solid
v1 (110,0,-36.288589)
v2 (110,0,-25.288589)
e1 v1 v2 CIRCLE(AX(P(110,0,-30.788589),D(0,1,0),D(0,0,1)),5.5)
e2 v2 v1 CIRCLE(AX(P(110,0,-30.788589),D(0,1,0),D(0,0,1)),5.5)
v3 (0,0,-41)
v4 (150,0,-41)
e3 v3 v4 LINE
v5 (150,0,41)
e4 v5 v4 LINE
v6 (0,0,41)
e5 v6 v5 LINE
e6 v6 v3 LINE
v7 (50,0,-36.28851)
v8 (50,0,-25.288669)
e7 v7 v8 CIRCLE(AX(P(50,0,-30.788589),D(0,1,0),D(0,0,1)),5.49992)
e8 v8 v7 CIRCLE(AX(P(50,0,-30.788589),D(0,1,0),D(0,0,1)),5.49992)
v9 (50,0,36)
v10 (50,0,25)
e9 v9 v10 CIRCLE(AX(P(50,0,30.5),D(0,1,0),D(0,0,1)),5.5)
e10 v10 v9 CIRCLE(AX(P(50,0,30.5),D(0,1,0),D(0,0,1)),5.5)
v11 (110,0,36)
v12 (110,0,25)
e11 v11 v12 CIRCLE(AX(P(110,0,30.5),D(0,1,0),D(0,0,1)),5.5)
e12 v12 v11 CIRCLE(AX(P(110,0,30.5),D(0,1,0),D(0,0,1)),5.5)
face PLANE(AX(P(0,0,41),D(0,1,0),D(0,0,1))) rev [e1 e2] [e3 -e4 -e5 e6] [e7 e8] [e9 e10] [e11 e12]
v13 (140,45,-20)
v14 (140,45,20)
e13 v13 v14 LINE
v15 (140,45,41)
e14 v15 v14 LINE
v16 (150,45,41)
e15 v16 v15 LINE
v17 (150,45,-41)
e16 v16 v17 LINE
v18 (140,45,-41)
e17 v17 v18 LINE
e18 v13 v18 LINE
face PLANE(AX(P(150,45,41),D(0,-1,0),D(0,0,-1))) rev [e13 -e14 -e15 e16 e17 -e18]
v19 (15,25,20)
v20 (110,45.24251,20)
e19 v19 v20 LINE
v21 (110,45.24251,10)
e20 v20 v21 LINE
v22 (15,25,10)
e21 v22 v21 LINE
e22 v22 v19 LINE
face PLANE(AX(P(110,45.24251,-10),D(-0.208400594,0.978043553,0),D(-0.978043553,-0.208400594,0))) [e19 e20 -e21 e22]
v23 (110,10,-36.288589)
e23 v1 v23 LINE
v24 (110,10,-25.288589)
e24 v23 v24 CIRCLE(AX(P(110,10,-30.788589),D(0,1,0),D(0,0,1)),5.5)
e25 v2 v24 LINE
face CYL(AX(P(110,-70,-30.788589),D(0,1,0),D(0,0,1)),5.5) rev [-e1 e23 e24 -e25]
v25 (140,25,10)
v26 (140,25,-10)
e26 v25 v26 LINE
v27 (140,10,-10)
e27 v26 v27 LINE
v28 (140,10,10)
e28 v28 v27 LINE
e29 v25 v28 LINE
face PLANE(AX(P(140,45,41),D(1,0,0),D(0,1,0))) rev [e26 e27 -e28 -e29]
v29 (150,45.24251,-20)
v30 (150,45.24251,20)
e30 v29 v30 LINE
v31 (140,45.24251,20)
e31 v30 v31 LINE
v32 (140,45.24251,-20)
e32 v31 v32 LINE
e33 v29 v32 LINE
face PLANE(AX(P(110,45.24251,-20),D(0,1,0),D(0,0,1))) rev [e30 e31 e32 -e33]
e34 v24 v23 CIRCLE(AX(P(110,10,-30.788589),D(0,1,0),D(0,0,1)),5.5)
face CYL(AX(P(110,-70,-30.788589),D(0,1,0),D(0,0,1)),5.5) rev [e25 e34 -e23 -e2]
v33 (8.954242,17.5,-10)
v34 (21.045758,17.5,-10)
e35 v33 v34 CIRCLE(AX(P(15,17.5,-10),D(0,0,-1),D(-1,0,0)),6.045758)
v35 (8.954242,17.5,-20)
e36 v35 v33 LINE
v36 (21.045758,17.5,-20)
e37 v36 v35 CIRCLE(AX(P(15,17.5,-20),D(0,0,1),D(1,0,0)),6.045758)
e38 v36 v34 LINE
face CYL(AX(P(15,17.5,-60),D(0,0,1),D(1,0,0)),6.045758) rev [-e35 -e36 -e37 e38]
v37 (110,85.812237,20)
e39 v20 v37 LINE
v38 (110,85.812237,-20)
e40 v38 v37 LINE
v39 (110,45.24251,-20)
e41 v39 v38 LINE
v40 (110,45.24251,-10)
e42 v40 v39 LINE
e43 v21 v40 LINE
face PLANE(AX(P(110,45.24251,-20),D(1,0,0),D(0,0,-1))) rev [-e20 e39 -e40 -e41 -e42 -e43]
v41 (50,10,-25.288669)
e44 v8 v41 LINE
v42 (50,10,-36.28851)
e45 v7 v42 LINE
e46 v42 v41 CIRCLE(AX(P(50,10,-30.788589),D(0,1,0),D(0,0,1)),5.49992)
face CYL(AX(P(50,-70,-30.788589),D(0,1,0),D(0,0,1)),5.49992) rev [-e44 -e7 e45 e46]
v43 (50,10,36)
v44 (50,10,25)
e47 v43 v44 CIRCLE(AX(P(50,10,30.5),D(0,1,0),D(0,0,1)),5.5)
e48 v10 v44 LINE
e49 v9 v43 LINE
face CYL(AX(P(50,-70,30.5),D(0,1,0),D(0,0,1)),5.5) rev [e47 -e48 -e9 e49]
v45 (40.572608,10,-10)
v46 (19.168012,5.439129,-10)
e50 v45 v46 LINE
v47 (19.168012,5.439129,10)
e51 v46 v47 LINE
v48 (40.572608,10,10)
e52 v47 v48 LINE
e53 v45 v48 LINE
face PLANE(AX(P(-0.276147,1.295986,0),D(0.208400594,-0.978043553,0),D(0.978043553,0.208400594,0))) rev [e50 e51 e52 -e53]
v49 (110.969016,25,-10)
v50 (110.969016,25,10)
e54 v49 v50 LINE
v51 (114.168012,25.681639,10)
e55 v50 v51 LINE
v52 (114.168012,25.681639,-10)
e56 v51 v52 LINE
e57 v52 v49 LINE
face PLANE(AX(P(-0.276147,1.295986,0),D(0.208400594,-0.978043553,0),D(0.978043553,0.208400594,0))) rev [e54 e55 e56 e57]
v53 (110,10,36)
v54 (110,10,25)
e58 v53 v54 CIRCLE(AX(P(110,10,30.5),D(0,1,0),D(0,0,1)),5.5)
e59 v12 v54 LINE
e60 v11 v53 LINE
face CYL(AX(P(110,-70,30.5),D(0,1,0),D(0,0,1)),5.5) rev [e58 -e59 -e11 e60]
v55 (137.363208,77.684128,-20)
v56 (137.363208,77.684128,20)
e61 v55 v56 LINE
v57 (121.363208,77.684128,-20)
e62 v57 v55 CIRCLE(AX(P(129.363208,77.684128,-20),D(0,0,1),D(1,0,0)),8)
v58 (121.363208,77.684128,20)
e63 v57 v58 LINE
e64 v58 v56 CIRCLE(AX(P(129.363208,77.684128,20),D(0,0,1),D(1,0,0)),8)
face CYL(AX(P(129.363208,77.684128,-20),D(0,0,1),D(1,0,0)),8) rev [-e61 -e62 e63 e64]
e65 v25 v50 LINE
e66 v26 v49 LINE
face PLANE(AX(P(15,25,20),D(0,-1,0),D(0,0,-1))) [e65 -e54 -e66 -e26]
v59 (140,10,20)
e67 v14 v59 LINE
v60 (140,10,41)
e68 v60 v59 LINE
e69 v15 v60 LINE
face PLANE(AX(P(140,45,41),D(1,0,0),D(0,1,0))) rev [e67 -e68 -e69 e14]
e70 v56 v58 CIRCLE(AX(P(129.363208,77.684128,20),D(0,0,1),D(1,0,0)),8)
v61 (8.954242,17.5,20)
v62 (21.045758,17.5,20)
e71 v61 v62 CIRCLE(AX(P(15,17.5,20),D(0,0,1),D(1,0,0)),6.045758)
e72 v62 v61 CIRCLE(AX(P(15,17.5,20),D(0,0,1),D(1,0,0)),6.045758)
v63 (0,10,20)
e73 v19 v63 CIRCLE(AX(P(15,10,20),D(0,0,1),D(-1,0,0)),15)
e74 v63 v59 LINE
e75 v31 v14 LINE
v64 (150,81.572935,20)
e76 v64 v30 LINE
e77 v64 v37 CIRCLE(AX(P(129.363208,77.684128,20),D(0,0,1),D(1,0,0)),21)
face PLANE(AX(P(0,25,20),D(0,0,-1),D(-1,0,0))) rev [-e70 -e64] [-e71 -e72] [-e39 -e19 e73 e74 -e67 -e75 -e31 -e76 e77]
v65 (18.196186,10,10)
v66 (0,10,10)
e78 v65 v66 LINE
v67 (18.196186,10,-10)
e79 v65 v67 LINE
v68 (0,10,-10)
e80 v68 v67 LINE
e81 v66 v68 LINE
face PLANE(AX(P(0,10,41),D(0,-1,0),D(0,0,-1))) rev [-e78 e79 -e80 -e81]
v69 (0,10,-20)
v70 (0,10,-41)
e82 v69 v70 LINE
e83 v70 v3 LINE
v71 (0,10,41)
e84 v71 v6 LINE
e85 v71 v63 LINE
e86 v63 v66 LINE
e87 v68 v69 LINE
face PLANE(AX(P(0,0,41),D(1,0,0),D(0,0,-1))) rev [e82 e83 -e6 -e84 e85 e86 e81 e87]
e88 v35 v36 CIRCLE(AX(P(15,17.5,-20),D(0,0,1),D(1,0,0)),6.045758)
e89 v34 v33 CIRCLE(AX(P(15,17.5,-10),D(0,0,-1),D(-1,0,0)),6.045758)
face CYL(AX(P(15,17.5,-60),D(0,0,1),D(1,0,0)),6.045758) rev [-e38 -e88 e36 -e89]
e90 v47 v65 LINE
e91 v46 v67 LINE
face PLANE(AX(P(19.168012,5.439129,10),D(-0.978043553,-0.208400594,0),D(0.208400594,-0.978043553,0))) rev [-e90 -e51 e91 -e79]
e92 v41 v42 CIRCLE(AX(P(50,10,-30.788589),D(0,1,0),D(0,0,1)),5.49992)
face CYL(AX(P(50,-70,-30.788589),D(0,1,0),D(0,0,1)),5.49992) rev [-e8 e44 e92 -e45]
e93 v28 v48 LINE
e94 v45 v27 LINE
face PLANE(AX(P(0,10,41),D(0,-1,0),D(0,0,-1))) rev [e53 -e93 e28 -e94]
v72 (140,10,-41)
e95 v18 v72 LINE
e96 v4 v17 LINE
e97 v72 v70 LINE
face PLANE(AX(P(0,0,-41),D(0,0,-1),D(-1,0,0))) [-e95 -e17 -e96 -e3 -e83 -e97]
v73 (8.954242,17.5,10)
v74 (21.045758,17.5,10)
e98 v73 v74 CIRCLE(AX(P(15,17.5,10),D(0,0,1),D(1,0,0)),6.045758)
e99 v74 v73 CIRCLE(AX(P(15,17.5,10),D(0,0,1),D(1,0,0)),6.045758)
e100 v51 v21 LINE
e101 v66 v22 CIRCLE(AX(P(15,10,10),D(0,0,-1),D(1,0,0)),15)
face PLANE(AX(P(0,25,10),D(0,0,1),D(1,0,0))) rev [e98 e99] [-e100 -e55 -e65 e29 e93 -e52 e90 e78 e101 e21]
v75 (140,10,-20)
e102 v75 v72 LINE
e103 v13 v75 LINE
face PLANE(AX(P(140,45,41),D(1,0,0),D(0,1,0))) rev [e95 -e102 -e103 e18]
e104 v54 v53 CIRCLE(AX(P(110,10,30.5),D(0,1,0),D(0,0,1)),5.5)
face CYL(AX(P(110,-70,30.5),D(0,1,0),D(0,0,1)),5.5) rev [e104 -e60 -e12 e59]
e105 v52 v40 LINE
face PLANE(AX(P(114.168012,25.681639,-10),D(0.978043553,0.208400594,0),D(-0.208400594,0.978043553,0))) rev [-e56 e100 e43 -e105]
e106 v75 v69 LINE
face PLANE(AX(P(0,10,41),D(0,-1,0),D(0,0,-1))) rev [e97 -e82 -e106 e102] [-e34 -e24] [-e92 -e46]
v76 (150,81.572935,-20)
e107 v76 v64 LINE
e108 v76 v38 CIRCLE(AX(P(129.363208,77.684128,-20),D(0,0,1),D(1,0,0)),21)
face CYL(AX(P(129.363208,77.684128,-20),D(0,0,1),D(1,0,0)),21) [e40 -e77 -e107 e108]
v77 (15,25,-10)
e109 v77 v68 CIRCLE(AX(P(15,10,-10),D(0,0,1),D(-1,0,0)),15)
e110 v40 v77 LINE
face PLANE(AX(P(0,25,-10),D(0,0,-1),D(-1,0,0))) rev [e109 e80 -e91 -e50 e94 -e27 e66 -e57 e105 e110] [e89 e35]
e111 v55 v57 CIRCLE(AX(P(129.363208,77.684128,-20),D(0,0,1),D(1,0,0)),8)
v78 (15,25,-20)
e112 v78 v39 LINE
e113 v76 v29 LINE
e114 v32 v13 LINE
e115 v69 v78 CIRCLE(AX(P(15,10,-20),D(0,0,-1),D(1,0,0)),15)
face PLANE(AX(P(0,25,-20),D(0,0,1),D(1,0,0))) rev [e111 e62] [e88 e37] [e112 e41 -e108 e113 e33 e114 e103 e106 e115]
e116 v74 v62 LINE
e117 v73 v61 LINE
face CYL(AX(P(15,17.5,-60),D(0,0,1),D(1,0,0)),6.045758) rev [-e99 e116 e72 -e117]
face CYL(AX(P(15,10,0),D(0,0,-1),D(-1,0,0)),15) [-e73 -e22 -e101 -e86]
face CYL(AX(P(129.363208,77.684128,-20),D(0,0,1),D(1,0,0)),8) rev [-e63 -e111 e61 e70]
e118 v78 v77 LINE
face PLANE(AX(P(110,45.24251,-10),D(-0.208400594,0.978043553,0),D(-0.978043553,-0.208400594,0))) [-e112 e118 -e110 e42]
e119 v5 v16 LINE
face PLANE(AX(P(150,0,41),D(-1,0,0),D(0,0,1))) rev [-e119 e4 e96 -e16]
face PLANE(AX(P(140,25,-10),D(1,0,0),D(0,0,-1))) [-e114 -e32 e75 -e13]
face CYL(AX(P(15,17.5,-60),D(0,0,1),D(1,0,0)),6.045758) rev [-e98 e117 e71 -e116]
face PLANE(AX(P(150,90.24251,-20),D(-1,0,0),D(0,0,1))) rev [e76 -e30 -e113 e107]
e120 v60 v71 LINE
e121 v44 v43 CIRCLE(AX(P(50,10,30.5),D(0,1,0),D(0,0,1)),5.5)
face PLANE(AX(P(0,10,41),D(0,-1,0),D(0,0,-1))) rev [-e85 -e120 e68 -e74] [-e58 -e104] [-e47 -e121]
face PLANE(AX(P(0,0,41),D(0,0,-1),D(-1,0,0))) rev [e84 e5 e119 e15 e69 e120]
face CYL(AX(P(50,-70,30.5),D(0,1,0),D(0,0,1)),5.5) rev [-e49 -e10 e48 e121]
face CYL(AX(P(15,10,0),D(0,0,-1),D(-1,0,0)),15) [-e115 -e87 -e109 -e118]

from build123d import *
from build123d.topology import SkipClean

# Parameters (mm, degrees)
BASE_ANGLE_PLATE_DEPTH           = 41
FORK_LUG_SKETCH_W                = 140
FORK_LUG_SKETCH_H                = 10
FORK_LUGS_DEPTH                  = 15
LUG_END_FILLET_R15_R             = 15
LUG_PIN_HOLE_SKETCH_R            = 6.045758047
LUG_PIN_HOLE_15_DEPTH            = 80
BASE_MOUNTING_HOLES_SKETCH_R     = 5.5
BASE_MOUNTING_HOLES_SKETCH_R_2   = 5.499920343
BASE_MOUNTING_HOLES_11_DEPTH     = 80
LUG_WEB_DEPTH                    = 10
ARM_PLATE_10MM_DEPTH             = 10
ARM_EXTENSION_40MM_DEPTH         = 40
UPRIGHT_BOSS_BLOCK_SKETCH_W      = 40
UPRIGHT_BOSS_BLOCK_SKETCH_H      = 45
UPRIGHT_BOSS_BLOCK_DEPTH         = 40
BEARING_BOSS_CLEARANCE_CUT_DEPTH = 40
BEARING_BOSS_DEPTH               = 40
BOSS_SLOT_SKETCH_W               = 97.132688683
BOSS_SLOT_SKETCH_H               = 20
BOSS_SLOT_CUT_20MM_DEPTH         = 20


with BuildPart() as part:
    # Base Angle Profile Sketch → Base Angle Plate (new, symmetric)
    with BuildSketch(Plane.XY):
        Polygon((0, 0), (150, 0), (150, 45), (140, 45), (140, 10), (0, 10), align=None)
    extrude(amount=BASE_ANGLE_PLATE_DEPTH, both=True)

    # Fork Lug Sketch → Fork Lugs (add)
    with BuildSketch(Plane(origin=(0, 10, 0), x_dir=(1, 0, 0), z_dir=(0, 1, 0))):
        with Locations((70, 15)):
            Rectangle(FORK_LUG_SKETCH_W, FORK_LUG_SKETCH_H)
        with Locations((70, -15)):
            Rectangle(FORK_LUG_SKETCH_W, FORK_LUG_SKETCH_H)
    extrude(amount=FORK_LUGS_DEPTH)

    # Lug End Fillet R15
    lug_end_fillet_r15_edges = [part.edges().sort_by_distance(p)[0] for p in [
        (0, 25, -15),
        (0, 25, 15),
    ]]
    fillet(lug_end_fillet_r15_edges, radius=LUG_END_FILLET_R15_R)

    # Lug Pin Hole Sketch → Lug Pin Hole _15 (cut)
    with BuildSketch(Plane.XY.offset(20)):
        with Locations((15, 17.5)):
            Circle(LUG_PIN_HOLE_SKETCH_R)
    extrude(amount=-LUG_PIN_HOLE_15_DEPTH, mode=Mode.SUBTRACT)

    # Base Mounting Holes Sketch → Base Mounting Holes _11 (cut)
    with BuildSketch(Plane(origin=(0, 10, 0), x_dir=(1, 0, 0), z_dir=(0, 1, 0))):
        with Locations(Location((110, -30.5, 0), (0, 0, 270))):
            Circle(BASE_MOUNTING_HOLES_SKETCH_R)
        with Locations(Location((50, -30.5, 0), (0, 0, 270))):
            Circle(BASE_MOUNTING_HOLES_SKETCH_R)
        with Locations(Location((110, 30.788589269, 0), (0, 0, 270))):
            Circle(BASE_MOUNTING_HOLES_SKETCH_R)
        with Locations(Location((50, 30.788589269, 0), (0, 0, 270))):
            Circle(BASE_MOUNTING_HOLES_SKETCH_R_2)
    extrude(amount=-BASE_MOUNTING_HOLES_11_DEPTH, mode=Mode.SUBTRACT)

    # Lug Web Sketch → Lug Web (add)
    with BuildSketch(Plane.XY.offset(20)):
        Polygon((109.382207464, 25), (109.382207464, 45), (15, 25), align=None)
    extrude(amount=-LUG_WEB_DEPTH)

    # Arm Profile Sketch → Arm Plate 10mm (add)
    with BuildSketch(Plane(origin=(0, 0, -20), x_dir=(-1, 0, 0), z_dir=(0, 0, -1))):
        Polygon((-140, 25), (-140, 45.242509992), (-110, 45.242509992), (-15, 25), align=None)
    extrude(amount=-ARM_PLATE_10MM_DEPTH)

    # Sketch17_3 → Arm Extension 40mm (add)
    with BuildSketch(Plane(origin=(0, 0, -20), x_dir=(-1, 0, 0), z_dir=(0, 0, -1))):
        Polygon((-140, 25), (-140, 45.242509992), (-110, 45.242509992), (-15, 25), align=None)
    extrude(amount=-ARM_EXTENSION_40MM_DEPTH)

    # Upright Boss Block Sketch → Upright Boss Block (add)
    with BuildSketch(Plane(origin=(110, 45.242509992, 20), x_dir=(-1, 0, 0), z_dir=(0, 0, -1))):
        with Locations((-20, 22.5)):
            Rectangle(UPRIGHT_BOSS_BLOCK_SKETCH_W, UPRIGHT_BOSS_BLOCK_SKETCH_H)
    extrude(amount=UPRIGHT_BOSS_BLOCK_DEPTH)

    # Bearing Boss Sketch → Bearing Boss Clearance Cut (cut)
    with BuildSketch(Plane.XY.offset(20)):
        with BuildLine():
            Line((137.363208202, 77.68412768), (129.363208202, 77.68412768))
            Line((129.363208202, 77.68412768), (121.363208202, 77.68412768))
            ThreePointArc((121.363208202, 77.68412768), (129.363208202, 69.68412768), (137.363208202, 77.68412768))
        make_face()
        with BuildLine():
            Line((121.363208202, 77.68412768), (129.363208202, 77.68412768))
            Line((129.363208202, 77.68412768), (137.363208202, 77.68412768))
            ThreePointArc((137.363208202, 77.68412768), (129.363208202, 85.68412768), (121.363208202, 77.68412768))
        make_face()
        with BuildLine():
            Line((137.363208202, 77.68412768), (129.363208202, 77.68412768))
            Line((129.363208202, 77.68412768), (121.363208202, 77.68412768))
            ThreePointArc((121.363208202, 77.68412768), (129.363208202, 69.68412768), (137.363208202, 77.68412768))
        make_face()
        with BuildLine():
            Line((121.363208202, 77.68412768), (129.363208202, 77.68412768))
            Line((129.363208202, 77.68412768), (137.363208202, 77.68412768))
            ThreePointArc((137.363208202, 77.68412768), (129.363208202, 85.68412768), (121.363208202, 77.68412768))
        make_face()
        with BuildLine():
            Line((110, 90.242509992), (110, 85.812237431))
            ThreePointArc((110, 85.812237431), (111.130972734, 88.104568642), (112.532075332, 90.242509992))
            Line((112.532075332, 90.242509992), (110, 90.242509992))
        make_face()
        with BuildLine():
            ThreePointArc((146.194341072, 90.242509992), (148.592137613, 86.12499693), (150, 81.572935245))
            Line((150, 81.572935245), (150, 90.242509992))
            Line((150, 90.242509992), (146.194341072, 90.242509992))
        make_face()
    extrude(amount=-BEARING_BOSS_CLEARANCE_CUT_DEPTH, mode=Mode.SUBTRACT)

    # Sketch20_3 → Bearing Boss (add)
    with SkipClean():  # the faces are left unmerged after this step: merging them gives an invalid solid
        with BuildSketch(Plane.XY.offset(20)):
            with BuildLine():
                ThreePointArc((146.194341072, 90.242509992), (129.363208202, 98.68412768), (112.532075332, 90.242509992))
                Line((112.532075332, 90.242509992), (146.194341072, 90.242509992))
            make_face()
        extrude(amount=-BEARING_BOSS_DEPTH)

    # Boss Slot Sketch → Boss Slot Cut 20mm (cut)
    with SkipClean():  # the faces are left unmerged after this step: merging them gives an invalid solid
        with BuildSketch(Plane(origin=(-4.444159319, 20.856856955, 0), x_dir=(0.9780435534944176, 0.20840059373238926, 0), z_dir=(-0.20840059373238926, 0.9780435534944176, 0))):
            with Locations((68.447012488, 0)):
                Rectangle(BOSS_SLOT_SKETCH_W, BOSS_SLOT_SKETCH_H)
        extrude(amount=-BOSS_SLOT_CUT_20MM_DEPTH, mode=Mode.SUBTRACT)


solid = part.part
